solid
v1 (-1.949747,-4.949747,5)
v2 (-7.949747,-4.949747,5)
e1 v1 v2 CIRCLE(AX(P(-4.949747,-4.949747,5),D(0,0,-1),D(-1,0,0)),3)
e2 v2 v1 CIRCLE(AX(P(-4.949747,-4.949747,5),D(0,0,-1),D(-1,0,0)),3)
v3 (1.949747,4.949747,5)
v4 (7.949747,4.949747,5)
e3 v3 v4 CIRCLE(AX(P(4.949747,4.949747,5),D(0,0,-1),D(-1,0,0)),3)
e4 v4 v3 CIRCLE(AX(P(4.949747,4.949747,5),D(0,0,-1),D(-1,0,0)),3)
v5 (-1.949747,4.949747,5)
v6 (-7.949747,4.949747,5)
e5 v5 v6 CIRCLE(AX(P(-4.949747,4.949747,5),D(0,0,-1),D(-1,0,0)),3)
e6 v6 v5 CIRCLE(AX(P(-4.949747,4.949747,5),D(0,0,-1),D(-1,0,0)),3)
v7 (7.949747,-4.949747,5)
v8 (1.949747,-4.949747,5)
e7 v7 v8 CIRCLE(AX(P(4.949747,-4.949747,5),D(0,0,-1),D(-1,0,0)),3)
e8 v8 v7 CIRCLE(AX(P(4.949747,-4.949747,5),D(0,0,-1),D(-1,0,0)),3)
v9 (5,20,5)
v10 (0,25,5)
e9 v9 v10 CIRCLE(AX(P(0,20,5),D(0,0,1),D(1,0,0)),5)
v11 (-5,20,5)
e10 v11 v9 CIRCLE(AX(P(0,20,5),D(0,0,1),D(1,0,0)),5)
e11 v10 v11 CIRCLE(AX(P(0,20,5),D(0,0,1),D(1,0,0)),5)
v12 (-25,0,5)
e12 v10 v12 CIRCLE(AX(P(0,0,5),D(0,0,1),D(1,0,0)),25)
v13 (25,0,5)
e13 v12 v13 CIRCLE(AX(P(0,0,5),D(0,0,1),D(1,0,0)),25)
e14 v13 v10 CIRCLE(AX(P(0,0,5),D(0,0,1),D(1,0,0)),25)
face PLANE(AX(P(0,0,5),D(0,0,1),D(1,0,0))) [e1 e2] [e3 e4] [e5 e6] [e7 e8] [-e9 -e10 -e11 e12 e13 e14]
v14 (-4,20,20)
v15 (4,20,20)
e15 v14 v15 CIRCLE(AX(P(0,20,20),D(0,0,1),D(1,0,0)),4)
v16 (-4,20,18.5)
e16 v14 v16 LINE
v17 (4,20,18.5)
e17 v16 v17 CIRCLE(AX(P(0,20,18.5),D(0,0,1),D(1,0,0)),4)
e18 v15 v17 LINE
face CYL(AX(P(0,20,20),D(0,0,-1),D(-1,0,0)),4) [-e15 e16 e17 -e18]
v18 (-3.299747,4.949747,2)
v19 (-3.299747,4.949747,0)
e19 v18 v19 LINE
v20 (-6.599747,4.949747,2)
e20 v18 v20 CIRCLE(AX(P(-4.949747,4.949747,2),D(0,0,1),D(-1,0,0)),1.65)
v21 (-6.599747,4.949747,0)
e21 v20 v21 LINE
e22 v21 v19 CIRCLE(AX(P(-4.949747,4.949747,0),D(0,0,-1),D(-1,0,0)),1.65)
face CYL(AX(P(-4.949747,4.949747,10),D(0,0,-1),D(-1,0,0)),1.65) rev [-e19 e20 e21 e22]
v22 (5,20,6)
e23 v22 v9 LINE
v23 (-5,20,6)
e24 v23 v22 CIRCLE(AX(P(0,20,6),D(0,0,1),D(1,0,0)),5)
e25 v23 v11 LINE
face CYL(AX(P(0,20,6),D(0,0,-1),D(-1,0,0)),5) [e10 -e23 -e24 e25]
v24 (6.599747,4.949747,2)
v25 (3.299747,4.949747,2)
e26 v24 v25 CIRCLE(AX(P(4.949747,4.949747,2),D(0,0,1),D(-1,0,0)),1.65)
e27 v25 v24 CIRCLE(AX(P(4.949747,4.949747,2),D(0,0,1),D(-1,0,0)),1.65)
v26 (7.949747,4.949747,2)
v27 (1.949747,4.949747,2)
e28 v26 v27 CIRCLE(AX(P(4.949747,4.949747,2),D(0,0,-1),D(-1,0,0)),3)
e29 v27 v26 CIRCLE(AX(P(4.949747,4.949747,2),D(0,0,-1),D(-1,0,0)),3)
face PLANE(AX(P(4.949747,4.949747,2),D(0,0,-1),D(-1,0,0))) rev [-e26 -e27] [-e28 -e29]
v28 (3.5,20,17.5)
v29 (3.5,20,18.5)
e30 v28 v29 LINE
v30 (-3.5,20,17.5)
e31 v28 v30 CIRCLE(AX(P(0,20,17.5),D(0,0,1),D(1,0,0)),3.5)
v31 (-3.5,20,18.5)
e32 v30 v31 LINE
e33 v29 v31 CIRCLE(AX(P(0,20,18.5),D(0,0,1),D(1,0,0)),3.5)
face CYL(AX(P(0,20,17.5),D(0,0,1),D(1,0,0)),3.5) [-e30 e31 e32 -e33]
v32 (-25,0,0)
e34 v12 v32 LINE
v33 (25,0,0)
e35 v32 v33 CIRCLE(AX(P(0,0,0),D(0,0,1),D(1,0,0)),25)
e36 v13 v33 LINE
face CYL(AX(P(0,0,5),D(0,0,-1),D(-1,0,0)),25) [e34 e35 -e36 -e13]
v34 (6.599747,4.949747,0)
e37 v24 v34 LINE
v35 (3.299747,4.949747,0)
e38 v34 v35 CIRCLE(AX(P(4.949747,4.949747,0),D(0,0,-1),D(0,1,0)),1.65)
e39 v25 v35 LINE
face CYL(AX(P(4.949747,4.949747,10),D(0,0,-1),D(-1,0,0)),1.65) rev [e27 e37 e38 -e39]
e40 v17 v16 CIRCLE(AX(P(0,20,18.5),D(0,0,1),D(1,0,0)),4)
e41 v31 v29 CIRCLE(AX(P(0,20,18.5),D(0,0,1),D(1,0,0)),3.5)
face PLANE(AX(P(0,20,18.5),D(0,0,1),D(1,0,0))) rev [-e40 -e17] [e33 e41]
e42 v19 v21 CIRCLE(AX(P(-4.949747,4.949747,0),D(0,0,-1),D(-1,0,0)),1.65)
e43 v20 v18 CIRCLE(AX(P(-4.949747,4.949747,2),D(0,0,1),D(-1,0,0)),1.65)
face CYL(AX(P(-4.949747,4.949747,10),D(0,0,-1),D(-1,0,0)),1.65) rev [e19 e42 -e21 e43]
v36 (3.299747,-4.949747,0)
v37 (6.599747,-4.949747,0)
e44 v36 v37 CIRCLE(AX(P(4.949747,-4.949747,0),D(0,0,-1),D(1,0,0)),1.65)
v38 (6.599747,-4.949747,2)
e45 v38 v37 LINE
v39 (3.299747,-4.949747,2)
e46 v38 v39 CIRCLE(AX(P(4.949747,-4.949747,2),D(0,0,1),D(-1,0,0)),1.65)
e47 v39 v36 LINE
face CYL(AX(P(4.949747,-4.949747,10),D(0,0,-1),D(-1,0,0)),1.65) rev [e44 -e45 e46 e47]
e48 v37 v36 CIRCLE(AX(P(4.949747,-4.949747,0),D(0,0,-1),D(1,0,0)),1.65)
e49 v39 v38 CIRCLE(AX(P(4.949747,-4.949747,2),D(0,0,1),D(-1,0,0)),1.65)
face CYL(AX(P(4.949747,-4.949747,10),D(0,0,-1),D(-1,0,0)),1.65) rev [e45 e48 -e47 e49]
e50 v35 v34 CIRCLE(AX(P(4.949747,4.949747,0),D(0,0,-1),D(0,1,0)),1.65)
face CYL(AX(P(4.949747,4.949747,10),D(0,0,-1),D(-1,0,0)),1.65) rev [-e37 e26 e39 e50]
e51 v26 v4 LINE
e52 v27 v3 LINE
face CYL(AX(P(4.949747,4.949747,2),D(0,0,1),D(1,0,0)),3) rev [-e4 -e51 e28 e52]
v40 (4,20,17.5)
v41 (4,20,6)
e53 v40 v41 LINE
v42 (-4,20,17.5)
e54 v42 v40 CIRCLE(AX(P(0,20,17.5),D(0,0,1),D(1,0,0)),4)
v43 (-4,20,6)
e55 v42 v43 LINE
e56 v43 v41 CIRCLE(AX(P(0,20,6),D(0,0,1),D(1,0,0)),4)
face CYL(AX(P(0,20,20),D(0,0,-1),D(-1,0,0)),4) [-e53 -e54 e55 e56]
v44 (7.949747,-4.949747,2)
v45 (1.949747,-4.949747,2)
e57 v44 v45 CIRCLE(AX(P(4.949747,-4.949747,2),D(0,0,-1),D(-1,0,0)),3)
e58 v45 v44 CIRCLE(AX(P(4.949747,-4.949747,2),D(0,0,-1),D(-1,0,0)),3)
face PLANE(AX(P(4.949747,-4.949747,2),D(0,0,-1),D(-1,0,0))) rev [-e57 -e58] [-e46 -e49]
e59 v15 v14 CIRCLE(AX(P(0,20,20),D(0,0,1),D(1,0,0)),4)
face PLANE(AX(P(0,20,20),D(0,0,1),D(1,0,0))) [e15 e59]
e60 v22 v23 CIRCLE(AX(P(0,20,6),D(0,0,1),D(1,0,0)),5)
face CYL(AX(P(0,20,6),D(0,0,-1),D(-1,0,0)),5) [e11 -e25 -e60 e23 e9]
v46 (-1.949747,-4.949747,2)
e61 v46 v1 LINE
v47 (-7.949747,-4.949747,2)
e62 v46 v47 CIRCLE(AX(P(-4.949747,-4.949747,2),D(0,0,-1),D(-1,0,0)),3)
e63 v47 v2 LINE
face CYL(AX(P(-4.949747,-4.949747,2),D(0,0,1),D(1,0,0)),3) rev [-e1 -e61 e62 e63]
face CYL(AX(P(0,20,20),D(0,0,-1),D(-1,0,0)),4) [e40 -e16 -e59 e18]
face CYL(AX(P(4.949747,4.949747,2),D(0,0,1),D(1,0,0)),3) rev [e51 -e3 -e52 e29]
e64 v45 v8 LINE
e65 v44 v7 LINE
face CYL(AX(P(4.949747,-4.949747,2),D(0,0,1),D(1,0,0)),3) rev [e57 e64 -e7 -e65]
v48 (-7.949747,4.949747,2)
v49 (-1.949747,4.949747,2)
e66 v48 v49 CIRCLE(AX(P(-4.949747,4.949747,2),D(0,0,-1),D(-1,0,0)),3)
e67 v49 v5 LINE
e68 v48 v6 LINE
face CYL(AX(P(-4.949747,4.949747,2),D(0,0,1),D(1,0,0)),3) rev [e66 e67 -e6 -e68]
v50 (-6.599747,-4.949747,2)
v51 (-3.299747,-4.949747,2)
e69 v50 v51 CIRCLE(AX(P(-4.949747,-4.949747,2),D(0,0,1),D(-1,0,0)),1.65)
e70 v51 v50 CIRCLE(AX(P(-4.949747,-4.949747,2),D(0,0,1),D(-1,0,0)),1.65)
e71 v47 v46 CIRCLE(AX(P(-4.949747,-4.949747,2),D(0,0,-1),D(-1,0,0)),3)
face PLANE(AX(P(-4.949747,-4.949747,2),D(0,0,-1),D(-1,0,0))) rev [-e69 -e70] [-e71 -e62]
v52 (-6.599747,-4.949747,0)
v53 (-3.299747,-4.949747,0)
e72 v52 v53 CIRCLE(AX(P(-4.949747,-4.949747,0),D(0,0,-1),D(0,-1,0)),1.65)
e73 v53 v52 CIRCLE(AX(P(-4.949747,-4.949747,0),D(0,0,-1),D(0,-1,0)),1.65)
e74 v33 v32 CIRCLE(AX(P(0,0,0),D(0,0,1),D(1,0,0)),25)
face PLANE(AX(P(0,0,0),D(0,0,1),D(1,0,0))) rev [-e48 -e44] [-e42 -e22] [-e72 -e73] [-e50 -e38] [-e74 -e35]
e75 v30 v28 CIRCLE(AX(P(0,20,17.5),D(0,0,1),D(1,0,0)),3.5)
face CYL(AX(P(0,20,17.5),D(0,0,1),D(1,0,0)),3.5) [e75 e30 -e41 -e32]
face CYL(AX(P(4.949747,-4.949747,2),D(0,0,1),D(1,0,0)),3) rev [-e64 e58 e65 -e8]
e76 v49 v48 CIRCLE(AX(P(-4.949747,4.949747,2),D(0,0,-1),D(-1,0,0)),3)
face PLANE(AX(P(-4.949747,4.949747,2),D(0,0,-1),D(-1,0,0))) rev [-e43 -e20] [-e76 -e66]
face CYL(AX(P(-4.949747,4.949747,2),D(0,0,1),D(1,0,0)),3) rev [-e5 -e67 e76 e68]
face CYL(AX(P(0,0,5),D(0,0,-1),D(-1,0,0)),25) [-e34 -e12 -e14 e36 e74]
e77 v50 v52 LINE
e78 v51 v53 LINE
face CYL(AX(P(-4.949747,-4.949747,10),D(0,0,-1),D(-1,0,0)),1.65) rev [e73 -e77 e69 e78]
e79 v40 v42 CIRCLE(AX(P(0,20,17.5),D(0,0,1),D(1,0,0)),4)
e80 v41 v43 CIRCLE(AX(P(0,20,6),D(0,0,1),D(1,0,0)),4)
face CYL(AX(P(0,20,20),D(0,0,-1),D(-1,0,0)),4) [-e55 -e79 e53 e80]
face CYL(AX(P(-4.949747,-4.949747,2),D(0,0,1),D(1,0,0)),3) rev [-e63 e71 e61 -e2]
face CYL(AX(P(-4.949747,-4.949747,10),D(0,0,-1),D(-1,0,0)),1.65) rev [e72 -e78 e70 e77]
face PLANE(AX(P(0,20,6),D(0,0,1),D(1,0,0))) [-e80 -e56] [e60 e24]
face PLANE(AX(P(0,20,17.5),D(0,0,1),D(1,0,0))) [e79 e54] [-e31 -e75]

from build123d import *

# Parameters (mm, degrees)
SKETCH_1_R               = 25
EXTRUDE_1_DEPTH          = 5
SKETCH_4_R               = 4
EXTRUDE_2_DEPTH          = 15
SKETCH_6_R               = 1.65
CUT_EXTRUDE_2_DEPTH      = 10
PATTERN_CIRCULAR_1_COUNT = 4
SKETCH_7_R               = 3
CUT_EXTRUDE_3_DEPTH      = 3
SKETCH_8_R               = 5
SKETCH_8_R_2             = 4
EXTRUDE_3_DEPTH          = 1
CUT_EXTRUDE_START        = -2.5
SKETCH_10_R              = 4
SKETCH_10_R_2            = 3.5
CUT_EXTRUDE_4_DEPTH      = 1


with BuildPart() as part:
    # 草图1 → 凸台-拉伸1 (new body)
    with BuildSketch(Plane.XY):
        Circle(SKETCH_1_R)
    extrude(amount=EXTRUDE_1_DEPTH)

    # 草图4 → 凸台-拉伸2 (add)
    with BuildSketch(Plane.XY.offset(5)):
        with Locations((0, 20)):
            Circle(SKETCH_4_R)
    extrude(amount=EXTRUDE_2_DEPTH)

    # 草图6 → 切除-拉伸2 (cut)
    with BuildSketch(Plane(origin=(0, 0, 0), x_dir=(-1, 0, 0), z_dir=(0, 0, -1))):
        with Locations((4.949747468, 4.949747468)):
            Circle(SKETCH_6_R)
    cut_extrude_2 = extrude(amount=-CUT_EXTRUDE_2_DEPTH, mode=Mode.SUBTRACT)

    # 阵列(圆周)1: 切除-拉伸2 ×4 about axis
    pattern_circular_1_axis = Axis((0, 0, 0), (0, 0, 1))
    for i in range(1, PATTERN_CIRCULAR_1_COUNT):
        add(cut_extrude_2.rotate(pattern_circular_1_axis, i * 360 / PATTERN_CIRCULAR_1_COUNT), mode=Mode.SUBTRACT)

    # 草图7 → 切除-拉伸3 (cut)
    with BuildSketch(Plane(origin=(0, 0, 5), x_dir=(-1, 0, 0), z_dir=(0, 0, -1))):
        with Locations((-4.949747468, 4.949747468)):
            Circle(SKETCH_7_R)
        with Locations((4.949747468, 4.949747468)):
            Circle(SKETCH_7_R)
        with Locations((4.949747468, -4.949747468)):
            Circle(SKETCH_7_R)
        with Locations((-4.949747468, -4.949747468)):
            Circle(SKETCH_7_R)
    extrude(amount=CUT_EXTRUDE_3_DEPTH, mode=Mode.SUBTRACT)

    # 草图8 → 凸台-拉伸3 (add)
    with BuildSketch(Plane.XY.offset(5)):
        with Locations(Location((0, 20, 0), (0, 0, 90))):
            Circle(SKETCH_8_R)
        with Locations((0, 20)):
            Circle(SKETCH_8_R_2, mode=Mode.SUBTRACT)
    extrude(amount=EXTRUDE_3_DEPTH)

    # 草图10 → 切除-拉伸4 (cut)
    with BuildSketch(Plane.XY.offset(20).offset(CUT_EXTRUDE_START)):
        with Locations((0, 20)):
            Circle(SKETCH_10_R)
        with Locations((0, 20)):
            Circle(SKETCH_10_R_2, mode=Mode.SUBTRACT)
    extrude(amount=CUT_EXTRUDE_4_DEPTH, mode=Mode.SUBTRACT)


solid = part.part
